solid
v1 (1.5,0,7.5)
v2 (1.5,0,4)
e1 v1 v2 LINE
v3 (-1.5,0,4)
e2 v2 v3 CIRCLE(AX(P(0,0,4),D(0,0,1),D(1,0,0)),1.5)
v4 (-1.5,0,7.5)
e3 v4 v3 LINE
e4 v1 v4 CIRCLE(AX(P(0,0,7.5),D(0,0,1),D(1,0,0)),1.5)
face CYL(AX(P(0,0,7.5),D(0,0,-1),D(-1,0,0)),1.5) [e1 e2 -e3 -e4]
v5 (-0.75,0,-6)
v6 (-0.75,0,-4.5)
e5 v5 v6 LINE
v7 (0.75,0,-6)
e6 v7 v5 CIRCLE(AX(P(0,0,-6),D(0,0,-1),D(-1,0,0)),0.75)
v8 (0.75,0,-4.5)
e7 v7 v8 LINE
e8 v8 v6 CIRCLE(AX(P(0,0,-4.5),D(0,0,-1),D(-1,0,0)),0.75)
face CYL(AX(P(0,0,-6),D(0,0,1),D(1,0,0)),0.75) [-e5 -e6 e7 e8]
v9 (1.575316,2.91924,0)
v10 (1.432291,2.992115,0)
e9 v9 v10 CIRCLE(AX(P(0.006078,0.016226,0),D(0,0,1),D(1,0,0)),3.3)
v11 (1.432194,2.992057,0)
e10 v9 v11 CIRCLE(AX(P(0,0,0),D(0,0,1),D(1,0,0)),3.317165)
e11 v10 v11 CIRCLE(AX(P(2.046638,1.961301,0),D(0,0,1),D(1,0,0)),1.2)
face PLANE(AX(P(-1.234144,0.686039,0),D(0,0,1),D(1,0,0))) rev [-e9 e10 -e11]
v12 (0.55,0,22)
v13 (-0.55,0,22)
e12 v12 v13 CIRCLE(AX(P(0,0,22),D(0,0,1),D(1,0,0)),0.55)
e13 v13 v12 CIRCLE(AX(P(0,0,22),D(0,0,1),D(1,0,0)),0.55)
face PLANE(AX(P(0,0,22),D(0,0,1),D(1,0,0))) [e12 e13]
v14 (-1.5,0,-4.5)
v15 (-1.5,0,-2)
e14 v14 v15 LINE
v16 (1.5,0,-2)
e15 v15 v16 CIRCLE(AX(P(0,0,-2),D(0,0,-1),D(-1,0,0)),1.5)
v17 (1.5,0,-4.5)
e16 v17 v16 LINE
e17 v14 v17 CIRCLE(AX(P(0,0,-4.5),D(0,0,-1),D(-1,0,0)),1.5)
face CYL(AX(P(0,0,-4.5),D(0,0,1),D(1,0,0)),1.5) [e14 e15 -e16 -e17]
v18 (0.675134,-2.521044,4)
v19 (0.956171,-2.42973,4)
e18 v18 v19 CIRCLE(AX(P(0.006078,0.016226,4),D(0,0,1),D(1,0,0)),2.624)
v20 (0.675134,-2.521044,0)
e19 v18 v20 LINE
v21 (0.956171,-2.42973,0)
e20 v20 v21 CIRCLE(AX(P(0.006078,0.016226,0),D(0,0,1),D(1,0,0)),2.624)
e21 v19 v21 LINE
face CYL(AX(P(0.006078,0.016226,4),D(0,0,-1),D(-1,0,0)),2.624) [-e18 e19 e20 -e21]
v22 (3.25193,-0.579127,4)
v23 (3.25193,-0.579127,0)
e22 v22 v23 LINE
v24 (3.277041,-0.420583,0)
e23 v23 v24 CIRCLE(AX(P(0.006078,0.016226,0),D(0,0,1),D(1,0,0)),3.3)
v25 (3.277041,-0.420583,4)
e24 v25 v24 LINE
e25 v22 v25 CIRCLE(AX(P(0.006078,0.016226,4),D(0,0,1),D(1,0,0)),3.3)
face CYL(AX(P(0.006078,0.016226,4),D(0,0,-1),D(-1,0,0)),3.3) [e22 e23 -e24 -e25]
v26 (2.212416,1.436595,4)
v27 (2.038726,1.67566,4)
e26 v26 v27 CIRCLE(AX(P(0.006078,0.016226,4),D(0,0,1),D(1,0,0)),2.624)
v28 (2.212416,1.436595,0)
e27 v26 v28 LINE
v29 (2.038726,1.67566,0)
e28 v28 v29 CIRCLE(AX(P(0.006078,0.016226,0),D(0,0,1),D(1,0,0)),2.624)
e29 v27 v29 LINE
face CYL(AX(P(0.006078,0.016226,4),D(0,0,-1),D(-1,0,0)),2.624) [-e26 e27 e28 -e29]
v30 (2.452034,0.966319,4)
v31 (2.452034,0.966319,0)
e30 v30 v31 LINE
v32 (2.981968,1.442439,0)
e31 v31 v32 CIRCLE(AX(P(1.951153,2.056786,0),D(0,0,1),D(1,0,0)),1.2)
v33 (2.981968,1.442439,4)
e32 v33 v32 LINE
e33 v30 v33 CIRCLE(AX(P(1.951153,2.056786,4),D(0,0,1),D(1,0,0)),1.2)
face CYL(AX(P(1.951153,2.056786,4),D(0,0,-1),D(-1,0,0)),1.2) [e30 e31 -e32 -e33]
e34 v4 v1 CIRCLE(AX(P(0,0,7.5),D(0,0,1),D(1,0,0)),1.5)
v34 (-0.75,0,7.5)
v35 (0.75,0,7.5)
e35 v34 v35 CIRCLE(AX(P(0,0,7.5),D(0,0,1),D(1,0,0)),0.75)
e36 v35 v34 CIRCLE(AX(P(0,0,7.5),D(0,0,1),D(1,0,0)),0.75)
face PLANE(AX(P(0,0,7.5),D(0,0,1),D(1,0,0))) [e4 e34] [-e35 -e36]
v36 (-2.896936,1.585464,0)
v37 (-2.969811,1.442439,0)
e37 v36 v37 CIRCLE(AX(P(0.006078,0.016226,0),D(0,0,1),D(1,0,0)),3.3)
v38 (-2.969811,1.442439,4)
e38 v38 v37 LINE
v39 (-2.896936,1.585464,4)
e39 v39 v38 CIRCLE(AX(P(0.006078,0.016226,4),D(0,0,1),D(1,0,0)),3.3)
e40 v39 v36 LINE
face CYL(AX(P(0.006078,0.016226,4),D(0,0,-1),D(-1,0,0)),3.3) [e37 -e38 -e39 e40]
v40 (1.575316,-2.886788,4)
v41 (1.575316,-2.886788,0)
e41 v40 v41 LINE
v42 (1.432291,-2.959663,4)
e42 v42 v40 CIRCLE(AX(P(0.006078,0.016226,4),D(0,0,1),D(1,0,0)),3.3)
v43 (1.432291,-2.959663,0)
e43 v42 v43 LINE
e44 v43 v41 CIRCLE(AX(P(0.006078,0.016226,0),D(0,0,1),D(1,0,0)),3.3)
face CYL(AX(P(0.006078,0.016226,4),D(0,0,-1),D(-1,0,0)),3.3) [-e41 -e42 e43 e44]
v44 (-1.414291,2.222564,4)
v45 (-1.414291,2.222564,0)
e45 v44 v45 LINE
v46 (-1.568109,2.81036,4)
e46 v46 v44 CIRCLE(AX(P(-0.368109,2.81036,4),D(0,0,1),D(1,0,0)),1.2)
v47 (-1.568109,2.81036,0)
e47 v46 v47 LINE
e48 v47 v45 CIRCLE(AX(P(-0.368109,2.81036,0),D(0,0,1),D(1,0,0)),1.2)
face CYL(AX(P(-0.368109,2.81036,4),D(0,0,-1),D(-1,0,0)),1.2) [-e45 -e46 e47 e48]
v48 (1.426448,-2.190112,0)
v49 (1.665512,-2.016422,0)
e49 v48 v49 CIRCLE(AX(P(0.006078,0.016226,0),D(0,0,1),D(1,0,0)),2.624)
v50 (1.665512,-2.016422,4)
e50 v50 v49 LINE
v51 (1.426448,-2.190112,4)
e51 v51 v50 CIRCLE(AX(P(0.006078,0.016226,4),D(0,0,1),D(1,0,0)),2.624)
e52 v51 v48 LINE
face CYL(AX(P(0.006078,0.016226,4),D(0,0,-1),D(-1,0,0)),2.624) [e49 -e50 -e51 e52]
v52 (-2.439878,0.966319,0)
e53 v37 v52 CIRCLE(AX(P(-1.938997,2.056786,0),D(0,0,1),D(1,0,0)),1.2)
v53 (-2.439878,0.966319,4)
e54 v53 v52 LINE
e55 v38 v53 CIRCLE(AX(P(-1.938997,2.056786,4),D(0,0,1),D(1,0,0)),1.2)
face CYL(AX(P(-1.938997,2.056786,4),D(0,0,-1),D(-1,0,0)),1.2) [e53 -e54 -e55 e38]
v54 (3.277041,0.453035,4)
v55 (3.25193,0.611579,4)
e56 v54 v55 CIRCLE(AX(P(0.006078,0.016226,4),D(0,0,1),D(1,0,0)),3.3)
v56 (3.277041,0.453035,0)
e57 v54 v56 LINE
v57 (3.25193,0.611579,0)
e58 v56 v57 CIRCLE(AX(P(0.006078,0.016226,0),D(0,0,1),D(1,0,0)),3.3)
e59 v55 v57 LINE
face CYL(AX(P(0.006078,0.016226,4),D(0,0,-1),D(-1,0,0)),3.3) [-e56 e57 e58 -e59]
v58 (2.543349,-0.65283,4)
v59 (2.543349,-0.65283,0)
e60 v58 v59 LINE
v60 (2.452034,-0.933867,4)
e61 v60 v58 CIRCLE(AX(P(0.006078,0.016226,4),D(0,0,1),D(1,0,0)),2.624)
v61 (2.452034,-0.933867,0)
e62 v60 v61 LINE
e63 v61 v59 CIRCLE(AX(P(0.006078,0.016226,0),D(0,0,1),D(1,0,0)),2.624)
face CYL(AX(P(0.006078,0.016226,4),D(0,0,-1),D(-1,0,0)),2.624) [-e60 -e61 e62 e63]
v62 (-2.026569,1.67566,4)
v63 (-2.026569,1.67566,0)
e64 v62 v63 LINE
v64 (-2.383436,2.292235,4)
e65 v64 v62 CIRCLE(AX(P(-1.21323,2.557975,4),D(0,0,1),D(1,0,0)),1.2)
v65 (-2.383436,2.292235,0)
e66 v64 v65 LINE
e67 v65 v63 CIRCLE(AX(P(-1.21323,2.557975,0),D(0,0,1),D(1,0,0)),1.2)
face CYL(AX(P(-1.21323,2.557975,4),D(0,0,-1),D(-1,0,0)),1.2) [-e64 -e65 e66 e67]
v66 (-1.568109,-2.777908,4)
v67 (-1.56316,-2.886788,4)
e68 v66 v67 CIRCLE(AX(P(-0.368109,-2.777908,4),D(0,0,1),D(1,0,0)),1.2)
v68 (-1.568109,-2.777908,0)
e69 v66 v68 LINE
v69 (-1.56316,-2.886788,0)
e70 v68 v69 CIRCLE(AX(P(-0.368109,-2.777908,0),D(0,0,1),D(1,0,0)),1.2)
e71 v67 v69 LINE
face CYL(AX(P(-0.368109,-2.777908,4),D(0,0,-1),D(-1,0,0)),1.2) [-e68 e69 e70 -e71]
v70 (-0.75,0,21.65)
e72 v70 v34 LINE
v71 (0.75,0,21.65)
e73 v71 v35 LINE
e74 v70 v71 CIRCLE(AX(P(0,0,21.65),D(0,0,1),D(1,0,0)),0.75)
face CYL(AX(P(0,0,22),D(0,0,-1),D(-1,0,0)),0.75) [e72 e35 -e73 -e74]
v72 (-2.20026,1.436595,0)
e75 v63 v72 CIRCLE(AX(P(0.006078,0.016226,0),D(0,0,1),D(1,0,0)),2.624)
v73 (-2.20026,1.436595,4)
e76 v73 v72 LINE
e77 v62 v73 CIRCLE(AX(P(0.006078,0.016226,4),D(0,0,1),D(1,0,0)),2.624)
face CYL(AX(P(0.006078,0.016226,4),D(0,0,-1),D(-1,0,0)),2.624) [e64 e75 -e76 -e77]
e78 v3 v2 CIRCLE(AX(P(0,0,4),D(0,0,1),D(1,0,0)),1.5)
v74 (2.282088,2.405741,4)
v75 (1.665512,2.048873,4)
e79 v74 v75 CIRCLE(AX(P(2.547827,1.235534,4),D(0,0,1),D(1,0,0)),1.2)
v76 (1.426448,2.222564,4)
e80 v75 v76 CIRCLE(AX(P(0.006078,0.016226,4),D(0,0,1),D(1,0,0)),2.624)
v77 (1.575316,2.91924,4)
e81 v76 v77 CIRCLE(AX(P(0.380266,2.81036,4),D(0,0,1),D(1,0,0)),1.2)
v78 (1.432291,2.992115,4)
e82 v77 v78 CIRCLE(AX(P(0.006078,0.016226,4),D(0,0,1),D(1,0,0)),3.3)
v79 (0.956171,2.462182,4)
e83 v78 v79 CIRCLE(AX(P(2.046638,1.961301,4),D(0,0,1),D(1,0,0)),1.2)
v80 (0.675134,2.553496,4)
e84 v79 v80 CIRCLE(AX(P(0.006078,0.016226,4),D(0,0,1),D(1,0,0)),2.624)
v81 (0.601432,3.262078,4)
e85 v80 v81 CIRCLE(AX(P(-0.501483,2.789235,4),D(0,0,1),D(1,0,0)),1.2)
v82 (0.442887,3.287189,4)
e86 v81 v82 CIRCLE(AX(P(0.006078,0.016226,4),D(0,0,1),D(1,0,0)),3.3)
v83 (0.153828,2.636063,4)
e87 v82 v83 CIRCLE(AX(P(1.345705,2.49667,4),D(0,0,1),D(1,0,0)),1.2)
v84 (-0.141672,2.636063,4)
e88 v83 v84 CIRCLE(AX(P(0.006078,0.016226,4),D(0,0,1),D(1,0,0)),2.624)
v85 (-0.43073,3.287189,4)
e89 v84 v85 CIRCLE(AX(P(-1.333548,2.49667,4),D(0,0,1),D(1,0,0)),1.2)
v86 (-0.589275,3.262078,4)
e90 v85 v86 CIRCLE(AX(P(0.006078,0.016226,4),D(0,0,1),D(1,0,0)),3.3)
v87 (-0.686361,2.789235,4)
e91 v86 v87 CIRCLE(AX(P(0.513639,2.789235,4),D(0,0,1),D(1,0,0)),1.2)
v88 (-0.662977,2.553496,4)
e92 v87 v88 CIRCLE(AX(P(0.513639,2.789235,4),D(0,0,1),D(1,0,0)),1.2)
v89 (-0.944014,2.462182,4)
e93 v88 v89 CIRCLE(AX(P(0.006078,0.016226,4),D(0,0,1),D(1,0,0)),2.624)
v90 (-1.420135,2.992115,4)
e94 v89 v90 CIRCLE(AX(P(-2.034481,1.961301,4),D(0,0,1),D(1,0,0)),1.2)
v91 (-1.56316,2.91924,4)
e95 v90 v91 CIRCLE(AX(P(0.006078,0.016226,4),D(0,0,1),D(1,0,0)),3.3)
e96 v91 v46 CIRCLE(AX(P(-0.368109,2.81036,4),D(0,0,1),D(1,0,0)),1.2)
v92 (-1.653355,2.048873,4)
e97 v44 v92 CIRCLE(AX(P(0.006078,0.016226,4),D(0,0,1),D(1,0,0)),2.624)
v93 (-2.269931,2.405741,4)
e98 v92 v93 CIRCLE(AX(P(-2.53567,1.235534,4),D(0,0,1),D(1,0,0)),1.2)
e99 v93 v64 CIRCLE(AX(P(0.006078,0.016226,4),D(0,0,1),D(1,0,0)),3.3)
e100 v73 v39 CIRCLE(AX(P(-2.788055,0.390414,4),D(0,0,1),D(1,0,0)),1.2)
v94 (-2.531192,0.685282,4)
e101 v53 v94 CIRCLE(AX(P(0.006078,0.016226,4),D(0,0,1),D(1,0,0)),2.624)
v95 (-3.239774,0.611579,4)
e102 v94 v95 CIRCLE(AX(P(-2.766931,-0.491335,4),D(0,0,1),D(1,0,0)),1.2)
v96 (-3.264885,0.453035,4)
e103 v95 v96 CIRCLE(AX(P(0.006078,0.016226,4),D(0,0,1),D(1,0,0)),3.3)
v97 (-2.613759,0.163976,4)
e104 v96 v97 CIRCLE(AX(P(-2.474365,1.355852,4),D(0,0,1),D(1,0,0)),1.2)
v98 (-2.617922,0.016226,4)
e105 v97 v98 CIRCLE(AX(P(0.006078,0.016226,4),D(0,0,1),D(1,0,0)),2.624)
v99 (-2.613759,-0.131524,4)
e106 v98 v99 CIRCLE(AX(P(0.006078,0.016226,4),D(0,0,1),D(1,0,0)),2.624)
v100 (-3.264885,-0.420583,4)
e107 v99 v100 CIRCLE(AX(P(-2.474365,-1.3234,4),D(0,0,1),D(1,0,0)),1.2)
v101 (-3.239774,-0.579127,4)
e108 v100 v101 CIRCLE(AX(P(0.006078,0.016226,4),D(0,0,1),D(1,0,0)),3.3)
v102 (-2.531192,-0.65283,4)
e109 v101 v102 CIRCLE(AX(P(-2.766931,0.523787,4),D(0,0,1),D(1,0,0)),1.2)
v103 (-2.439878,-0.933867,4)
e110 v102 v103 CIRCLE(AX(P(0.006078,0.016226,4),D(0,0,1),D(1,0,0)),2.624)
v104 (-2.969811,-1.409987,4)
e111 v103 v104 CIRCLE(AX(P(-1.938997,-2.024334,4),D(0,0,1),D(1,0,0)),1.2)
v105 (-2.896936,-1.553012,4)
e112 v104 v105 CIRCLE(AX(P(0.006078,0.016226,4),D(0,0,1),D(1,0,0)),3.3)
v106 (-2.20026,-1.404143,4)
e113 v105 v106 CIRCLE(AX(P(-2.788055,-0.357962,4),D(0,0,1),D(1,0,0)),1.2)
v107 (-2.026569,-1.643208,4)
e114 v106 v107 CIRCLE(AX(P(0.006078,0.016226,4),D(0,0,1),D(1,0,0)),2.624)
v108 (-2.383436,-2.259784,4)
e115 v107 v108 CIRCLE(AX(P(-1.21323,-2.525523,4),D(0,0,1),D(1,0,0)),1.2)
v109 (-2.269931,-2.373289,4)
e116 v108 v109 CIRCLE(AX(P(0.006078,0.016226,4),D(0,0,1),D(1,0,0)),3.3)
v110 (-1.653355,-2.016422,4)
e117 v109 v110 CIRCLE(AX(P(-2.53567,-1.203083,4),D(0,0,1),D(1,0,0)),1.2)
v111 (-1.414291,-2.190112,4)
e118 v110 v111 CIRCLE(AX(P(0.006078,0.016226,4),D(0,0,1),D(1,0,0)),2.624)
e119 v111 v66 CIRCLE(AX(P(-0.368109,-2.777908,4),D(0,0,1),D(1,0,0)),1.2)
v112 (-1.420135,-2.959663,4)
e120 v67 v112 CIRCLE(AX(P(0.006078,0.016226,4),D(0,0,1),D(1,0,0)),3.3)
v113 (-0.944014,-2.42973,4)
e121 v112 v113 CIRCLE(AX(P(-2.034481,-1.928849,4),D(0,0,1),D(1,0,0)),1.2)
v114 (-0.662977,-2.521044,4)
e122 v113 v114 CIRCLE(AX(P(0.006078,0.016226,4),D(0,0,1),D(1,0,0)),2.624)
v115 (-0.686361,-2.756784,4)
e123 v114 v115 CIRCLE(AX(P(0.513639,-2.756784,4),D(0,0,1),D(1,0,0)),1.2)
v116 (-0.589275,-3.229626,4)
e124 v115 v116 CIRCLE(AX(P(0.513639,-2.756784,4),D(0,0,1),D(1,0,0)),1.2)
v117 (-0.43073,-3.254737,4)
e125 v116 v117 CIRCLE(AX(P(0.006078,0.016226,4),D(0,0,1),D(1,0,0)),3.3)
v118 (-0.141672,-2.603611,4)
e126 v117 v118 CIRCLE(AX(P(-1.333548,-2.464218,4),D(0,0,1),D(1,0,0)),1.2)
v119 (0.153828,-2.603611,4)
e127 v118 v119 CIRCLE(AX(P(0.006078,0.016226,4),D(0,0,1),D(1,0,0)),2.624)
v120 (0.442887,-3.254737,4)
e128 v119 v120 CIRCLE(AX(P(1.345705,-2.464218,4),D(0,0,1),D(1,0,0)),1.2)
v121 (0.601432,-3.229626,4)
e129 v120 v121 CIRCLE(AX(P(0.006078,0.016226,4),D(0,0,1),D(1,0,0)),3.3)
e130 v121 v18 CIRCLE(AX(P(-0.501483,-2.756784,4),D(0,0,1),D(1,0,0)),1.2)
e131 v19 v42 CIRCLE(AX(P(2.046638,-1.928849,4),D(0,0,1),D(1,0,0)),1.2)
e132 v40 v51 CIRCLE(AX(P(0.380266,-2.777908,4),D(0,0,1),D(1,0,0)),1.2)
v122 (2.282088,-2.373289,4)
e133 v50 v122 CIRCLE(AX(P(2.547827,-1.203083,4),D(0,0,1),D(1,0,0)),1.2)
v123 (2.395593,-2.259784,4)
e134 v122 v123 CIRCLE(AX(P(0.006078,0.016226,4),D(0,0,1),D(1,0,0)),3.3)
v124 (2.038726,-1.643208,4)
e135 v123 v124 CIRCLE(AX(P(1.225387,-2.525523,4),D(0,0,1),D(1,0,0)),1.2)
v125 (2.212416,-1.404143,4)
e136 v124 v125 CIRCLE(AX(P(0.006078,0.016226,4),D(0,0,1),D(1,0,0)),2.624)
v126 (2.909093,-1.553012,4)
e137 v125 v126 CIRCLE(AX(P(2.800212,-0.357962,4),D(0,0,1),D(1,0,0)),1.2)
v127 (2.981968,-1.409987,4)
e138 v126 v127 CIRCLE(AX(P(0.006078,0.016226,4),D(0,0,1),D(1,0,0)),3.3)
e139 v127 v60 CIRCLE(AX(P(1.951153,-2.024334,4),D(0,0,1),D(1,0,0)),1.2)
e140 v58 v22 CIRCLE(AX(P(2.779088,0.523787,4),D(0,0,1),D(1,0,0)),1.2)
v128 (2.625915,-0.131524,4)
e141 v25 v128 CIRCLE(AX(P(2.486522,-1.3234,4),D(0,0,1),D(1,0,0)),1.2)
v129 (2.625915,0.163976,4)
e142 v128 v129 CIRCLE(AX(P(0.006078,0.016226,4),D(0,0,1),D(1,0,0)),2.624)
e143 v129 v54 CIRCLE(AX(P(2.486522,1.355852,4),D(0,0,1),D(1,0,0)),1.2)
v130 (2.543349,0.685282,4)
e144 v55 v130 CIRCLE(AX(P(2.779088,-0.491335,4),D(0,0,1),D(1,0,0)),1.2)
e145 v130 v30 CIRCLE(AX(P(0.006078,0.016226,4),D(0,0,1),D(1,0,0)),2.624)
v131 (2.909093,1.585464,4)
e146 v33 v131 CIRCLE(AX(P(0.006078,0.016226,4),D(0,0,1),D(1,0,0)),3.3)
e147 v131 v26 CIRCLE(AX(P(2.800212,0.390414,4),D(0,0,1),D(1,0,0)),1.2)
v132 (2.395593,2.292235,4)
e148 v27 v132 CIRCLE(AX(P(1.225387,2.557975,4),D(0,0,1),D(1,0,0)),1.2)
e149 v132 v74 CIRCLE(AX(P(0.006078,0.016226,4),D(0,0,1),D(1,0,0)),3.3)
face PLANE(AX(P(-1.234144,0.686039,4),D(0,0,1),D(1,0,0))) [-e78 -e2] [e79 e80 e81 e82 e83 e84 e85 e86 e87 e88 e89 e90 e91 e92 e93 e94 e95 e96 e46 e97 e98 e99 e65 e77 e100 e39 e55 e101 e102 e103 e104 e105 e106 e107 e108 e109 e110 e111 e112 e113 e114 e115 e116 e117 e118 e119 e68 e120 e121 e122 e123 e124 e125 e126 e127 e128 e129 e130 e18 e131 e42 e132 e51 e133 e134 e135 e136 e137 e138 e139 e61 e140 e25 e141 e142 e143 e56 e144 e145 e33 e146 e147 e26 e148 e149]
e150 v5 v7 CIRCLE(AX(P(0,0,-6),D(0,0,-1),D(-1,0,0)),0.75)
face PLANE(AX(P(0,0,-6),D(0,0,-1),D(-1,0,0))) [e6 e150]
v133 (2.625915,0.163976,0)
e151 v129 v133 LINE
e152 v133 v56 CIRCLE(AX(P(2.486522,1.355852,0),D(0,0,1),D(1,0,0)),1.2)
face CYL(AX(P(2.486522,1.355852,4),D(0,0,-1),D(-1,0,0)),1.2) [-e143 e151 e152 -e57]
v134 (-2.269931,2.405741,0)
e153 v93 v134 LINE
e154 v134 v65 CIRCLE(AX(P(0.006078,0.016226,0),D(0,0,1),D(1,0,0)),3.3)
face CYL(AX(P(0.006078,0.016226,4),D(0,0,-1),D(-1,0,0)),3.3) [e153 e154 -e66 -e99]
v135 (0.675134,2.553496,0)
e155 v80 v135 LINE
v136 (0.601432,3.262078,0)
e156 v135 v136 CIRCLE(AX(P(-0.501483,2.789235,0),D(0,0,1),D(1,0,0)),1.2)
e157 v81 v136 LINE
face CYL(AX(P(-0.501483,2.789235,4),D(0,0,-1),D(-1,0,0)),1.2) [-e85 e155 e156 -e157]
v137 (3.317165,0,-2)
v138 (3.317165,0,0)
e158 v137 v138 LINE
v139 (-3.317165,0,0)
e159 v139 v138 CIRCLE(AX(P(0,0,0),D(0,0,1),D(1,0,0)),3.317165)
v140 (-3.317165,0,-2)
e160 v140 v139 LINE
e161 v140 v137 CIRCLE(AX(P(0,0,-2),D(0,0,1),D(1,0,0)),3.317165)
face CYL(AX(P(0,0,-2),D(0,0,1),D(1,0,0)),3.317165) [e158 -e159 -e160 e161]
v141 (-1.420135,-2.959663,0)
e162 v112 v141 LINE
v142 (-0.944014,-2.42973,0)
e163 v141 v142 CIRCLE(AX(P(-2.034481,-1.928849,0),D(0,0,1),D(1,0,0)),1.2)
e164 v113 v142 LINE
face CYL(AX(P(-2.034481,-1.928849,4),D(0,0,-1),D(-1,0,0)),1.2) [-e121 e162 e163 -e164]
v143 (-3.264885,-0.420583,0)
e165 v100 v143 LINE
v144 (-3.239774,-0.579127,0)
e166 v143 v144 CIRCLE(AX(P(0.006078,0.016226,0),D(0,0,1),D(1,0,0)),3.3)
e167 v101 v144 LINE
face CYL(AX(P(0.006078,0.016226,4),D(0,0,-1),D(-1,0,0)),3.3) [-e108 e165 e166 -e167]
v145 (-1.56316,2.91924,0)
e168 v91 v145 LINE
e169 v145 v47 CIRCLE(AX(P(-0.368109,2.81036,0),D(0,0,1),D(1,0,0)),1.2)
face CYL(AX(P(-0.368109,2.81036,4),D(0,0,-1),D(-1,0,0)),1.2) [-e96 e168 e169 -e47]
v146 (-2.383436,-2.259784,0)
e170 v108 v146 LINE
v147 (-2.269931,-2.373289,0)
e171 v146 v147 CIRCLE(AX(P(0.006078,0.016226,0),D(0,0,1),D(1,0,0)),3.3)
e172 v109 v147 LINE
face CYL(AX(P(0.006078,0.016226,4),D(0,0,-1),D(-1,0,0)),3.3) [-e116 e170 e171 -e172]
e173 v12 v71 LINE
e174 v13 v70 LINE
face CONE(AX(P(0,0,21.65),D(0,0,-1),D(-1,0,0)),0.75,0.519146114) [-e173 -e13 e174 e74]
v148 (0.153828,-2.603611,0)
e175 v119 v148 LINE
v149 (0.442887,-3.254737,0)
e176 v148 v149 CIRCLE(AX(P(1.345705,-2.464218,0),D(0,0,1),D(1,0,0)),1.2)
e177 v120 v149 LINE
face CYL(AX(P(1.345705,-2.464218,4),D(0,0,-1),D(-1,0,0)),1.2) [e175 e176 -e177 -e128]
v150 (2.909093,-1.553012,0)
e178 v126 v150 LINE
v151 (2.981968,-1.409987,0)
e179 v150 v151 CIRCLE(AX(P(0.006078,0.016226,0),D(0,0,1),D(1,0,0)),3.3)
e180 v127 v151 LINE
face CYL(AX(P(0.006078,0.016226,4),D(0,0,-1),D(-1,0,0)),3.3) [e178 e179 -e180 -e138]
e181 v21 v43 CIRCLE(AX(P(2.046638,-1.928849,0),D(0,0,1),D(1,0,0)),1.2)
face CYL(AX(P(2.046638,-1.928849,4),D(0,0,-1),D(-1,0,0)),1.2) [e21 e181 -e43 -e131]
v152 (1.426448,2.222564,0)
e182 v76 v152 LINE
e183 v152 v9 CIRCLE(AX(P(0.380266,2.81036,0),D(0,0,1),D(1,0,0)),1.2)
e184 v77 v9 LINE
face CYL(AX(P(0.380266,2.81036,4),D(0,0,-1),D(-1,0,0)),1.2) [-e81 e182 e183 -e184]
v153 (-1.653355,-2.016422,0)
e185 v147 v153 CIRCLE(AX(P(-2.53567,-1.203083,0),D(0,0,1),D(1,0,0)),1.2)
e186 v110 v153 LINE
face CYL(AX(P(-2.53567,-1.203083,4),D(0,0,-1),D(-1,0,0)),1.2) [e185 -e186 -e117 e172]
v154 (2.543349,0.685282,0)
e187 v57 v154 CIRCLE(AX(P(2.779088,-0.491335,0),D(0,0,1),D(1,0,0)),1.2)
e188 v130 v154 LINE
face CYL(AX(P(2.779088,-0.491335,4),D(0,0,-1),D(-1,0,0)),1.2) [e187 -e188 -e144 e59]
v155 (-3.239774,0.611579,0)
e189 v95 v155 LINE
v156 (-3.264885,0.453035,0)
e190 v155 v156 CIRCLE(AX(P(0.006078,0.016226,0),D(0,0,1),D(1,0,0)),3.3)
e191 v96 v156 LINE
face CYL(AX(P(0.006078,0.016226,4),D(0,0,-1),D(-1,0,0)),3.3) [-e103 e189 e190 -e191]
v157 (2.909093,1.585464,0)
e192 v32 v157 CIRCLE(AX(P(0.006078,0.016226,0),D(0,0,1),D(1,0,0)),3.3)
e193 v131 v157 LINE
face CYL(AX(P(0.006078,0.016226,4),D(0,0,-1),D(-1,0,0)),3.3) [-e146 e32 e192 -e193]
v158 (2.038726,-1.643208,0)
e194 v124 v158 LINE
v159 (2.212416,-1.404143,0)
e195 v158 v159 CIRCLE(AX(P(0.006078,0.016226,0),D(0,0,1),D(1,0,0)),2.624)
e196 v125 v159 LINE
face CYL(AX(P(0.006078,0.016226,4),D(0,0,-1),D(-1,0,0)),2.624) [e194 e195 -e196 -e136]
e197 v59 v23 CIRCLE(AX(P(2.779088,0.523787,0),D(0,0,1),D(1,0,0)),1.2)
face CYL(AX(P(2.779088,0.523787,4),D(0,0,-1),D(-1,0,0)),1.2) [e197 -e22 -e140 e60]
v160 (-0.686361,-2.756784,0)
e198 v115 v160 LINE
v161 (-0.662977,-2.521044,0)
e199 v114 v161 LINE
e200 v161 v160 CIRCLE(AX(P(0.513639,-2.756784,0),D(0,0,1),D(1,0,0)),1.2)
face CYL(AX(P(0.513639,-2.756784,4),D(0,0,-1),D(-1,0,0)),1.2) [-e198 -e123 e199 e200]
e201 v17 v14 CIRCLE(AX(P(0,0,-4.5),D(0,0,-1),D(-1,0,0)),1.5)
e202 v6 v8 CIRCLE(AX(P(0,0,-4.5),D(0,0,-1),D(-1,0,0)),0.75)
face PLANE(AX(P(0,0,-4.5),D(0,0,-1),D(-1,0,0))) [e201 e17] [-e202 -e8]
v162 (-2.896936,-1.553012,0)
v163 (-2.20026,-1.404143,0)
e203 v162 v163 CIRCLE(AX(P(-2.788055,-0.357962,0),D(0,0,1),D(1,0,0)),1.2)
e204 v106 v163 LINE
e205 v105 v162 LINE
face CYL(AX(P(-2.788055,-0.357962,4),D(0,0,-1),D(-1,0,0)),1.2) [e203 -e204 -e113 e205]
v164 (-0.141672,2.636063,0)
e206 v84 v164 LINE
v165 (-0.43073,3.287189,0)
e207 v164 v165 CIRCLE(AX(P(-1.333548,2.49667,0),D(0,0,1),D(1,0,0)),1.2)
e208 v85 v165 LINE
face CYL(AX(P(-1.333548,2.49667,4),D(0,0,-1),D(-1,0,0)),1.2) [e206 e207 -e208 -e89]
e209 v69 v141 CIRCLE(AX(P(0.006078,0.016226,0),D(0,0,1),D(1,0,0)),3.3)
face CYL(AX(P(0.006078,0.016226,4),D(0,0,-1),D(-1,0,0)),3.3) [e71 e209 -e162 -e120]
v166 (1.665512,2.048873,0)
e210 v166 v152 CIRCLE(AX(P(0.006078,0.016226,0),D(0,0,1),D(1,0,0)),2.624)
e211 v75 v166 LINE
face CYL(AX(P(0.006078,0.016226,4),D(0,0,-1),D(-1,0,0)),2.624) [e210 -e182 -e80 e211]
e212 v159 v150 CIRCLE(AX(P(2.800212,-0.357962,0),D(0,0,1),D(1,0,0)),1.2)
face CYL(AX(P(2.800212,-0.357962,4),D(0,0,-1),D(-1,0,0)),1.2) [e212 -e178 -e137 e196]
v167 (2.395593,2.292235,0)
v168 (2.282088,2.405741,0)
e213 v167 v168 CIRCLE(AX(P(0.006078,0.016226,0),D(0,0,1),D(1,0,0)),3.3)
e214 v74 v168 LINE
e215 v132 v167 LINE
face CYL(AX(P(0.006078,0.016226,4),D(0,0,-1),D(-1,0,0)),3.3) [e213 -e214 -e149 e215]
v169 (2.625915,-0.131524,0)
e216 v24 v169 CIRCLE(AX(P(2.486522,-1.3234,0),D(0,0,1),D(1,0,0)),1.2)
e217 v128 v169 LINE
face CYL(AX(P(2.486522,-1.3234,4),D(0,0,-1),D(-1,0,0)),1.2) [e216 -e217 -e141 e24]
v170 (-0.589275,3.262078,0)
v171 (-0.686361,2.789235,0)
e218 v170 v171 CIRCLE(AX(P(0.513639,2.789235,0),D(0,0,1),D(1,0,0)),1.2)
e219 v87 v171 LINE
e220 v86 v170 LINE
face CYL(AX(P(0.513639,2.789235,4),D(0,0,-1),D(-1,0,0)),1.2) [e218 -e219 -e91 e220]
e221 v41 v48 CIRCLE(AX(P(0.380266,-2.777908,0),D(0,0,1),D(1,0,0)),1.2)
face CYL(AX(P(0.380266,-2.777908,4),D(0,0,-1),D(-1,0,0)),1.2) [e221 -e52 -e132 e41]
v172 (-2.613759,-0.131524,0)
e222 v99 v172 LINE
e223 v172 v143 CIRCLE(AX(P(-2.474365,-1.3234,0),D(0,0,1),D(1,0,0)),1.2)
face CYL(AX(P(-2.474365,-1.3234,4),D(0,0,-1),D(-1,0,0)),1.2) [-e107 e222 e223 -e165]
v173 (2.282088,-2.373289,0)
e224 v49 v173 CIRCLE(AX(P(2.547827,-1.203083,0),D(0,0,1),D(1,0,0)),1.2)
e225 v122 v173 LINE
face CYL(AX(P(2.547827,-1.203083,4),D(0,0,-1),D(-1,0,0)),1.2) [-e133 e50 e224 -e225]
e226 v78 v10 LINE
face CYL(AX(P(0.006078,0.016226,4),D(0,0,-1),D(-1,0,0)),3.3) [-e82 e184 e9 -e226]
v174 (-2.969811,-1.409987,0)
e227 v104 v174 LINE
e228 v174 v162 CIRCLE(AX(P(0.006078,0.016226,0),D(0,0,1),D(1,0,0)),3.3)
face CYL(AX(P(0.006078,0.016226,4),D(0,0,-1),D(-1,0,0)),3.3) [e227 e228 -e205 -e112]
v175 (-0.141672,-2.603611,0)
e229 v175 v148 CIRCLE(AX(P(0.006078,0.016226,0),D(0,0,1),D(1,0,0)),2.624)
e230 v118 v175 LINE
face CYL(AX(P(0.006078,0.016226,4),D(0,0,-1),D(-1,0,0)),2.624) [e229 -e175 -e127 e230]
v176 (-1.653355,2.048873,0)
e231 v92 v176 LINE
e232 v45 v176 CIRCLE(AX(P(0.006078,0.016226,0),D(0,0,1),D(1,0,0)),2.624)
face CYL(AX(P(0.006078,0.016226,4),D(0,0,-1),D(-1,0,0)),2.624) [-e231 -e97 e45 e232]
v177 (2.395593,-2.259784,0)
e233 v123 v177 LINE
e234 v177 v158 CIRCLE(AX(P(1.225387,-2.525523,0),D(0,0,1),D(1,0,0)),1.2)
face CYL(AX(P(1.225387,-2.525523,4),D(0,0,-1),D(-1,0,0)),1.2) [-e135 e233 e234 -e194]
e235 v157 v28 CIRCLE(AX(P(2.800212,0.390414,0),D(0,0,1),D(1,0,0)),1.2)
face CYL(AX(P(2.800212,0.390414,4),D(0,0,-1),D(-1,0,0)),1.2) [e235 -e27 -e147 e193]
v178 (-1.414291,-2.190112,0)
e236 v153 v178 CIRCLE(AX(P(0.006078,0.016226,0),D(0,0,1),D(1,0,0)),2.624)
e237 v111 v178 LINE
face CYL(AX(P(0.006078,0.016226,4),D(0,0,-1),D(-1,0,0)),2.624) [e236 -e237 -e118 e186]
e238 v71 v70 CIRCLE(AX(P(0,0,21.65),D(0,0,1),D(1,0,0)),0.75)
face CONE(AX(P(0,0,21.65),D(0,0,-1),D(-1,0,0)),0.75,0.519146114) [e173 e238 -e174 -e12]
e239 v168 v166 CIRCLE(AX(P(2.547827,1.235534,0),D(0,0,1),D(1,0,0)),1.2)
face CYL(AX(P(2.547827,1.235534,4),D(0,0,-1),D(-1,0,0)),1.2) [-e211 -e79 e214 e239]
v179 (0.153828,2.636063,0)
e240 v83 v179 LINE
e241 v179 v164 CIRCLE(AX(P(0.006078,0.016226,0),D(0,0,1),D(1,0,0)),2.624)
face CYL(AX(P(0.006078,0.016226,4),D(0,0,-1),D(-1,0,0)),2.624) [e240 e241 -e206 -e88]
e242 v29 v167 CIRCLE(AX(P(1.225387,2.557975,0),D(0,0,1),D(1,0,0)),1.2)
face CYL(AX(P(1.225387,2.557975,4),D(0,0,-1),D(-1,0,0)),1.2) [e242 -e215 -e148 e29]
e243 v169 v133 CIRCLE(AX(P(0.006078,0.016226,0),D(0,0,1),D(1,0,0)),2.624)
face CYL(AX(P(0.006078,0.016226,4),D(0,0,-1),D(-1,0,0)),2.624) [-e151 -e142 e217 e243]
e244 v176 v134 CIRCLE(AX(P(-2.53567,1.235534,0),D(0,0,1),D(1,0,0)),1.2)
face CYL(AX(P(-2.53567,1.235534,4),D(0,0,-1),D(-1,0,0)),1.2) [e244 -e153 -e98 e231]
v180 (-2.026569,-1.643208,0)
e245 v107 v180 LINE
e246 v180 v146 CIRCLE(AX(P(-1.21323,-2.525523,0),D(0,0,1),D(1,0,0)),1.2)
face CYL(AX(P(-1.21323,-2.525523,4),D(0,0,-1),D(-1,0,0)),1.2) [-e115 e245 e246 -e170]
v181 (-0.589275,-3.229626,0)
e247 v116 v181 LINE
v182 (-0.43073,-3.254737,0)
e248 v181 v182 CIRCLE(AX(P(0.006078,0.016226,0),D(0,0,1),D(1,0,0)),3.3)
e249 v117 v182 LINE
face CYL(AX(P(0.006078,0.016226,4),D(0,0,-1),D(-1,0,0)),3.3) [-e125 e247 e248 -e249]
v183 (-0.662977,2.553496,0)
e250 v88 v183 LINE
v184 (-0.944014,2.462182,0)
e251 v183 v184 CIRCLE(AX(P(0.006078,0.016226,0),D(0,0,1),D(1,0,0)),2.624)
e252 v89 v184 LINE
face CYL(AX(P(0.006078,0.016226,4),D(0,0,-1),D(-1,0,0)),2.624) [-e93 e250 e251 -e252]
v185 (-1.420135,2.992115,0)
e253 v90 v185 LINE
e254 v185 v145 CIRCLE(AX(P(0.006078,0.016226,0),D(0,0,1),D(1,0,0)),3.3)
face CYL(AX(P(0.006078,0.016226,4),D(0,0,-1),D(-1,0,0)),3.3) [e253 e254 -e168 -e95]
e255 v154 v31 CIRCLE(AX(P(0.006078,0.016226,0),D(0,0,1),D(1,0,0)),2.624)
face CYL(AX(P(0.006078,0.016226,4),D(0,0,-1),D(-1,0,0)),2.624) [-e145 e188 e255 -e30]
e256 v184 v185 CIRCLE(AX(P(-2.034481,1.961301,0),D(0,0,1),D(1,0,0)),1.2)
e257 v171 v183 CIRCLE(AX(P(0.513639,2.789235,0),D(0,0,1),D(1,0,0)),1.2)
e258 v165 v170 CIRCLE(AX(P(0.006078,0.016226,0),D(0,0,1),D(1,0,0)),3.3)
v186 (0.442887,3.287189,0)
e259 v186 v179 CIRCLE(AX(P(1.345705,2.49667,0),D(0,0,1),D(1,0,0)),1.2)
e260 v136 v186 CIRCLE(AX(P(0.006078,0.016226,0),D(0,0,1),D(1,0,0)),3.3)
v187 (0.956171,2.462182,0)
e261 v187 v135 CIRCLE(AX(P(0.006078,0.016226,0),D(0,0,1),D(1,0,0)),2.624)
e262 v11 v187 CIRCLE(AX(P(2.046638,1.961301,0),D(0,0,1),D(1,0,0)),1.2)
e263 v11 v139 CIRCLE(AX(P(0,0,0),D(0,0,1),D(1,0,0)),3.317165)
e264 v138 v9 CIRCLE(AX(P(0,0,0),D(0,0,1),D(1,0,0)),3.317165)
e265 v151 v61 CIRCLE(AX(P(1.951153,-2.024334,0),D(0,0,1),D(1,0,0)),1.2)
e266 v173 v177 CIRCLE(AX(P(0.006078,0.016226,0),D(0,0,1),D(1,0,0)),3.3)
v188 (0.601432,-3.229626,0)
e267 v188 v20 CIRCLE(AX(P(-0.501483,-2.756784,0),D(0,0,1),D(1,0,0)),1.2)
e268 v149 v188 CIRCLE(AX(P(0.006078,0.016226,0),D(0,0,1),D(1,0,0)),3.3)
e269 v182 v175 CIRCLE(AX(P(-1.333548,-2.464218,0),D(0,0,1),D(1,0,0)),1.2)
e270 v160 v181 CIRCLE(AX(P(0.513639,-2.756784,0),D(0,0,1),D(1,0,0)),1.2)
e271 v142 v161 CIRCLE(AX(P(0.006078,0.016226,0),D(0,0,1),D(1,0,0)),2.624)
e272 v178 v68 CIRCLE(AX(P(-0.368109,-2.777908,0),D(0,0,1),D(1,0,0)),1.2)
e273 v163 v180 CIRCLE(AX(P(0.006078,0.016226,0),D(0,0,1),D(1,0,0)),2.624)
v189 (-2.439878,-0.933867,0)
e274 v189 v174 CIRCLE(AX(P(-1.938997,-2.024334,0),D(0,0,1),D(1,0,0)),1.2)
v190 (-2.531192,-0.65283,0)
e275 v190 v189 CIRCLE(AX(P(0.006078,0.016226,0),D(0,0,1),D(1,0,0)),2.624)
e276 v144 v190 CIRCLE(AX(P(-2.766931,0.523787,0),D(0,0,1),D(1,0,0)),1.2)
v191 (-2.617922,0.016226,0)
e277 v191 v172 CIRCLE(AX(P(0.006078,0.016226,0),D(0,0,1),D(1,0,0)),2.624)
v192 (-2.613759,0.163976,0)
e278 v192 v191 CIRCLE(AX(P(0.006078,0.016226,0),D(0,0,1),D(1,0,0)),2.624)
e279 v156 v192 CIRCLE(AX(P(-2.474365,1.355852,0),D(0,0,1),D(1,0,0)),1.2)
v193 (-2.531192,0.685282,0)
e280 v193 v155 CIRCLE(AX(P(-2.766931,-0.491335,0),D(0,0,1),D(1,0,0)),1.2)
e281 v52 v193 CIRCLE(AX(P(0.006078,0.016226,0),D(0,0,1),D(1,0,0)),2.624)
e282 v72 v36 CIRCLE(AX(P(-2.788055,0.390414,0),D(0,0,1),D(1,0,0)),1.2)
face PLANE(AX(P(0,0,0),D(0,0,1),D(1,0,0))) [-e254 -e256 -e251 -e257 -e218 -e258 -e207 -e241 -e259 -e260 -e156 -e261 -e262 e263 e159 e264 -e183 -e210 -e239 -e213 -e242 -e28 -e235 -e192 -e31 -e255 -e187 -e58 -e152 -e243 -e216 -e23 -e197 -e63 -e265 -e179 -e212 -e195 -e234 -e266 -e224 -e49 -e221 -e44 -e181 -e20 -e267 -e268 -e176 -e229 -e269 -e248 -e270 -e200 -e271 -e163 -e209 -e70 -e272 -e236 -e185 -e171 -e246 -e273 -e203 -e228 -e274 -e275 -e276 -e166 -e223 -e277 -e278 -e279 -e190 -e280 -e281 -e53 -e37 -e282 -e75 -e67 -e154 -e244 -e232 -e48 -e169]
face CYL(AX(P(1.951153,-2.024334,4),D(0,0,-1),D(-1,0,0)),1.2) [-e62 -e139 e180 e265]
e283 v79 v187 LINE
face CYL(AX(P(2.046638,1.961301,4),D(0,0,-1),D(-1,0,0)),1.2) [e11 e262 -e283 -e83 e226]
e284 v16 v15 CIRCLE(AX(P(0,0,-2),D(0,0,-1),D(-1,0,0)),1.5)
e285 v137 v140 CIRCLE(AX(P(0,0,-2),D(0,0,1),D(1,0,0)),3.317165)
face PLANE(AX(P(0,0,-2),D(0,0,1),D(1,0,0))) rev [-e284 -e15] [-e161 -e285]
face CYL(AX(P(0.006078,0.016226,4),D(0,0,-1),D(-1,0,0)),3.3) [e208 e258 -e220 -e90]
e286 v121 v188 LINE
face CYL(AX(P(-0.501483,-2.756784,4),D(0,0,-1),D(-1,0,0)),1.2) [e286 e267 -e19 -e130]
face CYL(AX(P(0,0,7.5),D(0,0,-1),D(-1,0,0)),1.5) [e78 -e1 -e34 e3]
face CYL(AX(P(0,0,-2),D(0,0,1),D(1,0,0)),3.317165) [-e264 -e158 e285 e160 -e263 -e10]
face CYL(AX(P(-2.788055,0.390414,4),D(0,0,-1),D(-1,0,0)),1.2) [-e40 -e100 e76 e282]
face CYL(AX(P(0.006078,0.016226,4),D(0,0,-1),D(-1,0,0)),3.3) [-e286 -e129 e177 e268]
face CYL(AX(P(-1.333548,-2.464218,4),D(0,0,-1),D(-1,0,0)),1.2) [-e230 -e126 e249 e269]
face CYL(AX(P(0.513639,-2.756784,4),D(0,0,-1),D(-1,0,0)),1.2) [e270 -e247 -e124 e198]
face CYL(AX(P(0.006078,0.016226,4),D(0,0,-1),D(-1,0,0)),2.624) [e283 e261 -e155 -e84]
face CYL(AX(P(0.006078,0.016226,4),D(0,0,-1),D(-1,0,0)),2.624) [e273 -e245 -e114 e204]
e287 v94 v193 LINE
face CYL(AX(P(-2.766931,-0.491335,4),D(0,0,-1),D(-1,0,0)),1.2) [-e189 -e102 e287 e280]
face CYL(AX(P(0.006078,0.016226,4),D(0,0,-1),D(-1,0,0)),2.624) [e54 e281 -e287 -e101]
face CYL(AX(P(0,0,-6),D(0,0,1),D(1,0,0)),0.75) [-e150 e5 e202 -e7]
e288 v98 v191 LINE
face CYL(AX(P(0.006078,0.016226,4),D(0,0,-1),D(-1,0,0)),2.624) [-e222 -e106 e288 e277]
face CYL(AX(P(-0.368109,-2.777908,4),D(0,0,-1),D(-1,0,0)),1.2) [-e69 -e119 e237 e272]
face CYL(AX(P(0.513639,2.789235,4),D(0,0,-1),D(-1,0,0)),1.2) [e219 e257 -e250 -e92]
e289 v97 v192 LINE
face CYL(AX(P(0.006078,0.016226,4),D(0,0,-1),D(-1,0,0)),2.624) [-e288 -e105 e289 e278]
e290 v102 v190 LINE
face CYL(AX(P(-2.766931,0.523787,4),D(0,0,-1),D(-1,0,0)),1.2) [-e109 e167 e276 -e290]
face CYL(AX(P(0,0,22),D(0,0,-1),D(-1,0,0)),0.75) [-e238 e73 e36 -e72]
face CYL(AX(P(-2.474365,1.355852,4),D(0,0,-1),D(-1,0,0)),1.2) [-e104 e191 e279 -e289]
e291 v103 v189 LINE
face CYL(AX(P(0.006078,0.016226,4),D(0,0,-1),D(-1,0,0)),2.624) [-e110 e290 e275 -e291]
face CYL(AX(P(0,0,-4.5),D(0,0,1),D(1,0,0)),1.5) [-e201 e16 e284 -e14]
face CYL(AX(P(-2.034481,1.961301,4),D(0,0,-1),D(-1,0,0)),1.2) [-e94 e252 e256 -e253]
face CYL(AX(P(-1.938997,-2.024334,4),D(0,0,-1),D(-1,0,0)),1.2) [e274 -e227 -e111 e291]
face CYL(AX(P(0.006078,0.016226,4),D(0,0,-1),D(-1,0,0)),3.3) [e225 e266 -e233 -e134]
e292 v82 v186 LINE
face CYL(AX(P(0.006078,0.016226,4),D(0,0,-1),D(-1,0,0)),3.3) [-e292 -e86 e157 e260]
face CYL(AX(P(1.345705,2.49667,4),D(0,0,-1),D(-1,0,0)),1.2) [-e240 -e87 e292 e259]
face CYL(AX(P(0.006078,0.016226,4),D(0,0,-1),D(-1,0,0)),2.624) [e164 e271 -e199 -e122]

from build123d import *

# Parameters (mm, degrees)
BOSS_EXTRUDE_1_DEPTH = 4
SKETCH_3_R           = 3.317165214
BOSS_EXTRUDE_2_DEPTH = 2
SKETCH_4_R           = 1.5
BOSS_EXTRUDE_3_DEPTH = 2.5
BOSS_EXTRUDE_START   = 3.5
SKETCH_5_R           = 1.5
BOSS_EXTRUDE_4_DEPTH = 3.5
SKETCH_6_R           = 0.75
BOSS_EXTRUDE_5_DEPTH = 1.5
BOSS_EXTRUDE_START_2 = 14.5
SKETCH_7_R           = 0.75
BOSS_EXTRUDE_6_DEPTH = 14.5


with BuildPart() as part:
    # Sketch 1 → Boss-Extrude 1 (new body)
    with BuildSketch(Plane.XY):
        with BuildLine():
            ThreePointArc((-3.264884569, 0.453034732), (-2.961266903, 0.259072006), (-2.613758715, 0.163975816))
            ThreePointArc((-2.613758715, 0.163975816), (-2.617921702, 0.016225934), (-2.613758715, -0.131523948))
            ThreePointArc((-2.613758715, -0.131523948), (-2.961266903, -0.226620138), (-3.264884569, -0.420582864))
            ThreePointArc((-3.264884569, -0.420582864), (-3.253293226, -0.500007801), (-3.239773593, -0.579127326))
            ThreePointArc((-3.239773593, -0.579127326), (-2.891078254, -0.669773822), (-2.531191989, -0.652829737))
            ThreePointArc((-2.531191989, -0.652829737), (-2.489494001, -0.794634659), (-2.43987754, -0.933866714))
            ThreePointArc((-2.43987754, -0.933866714), (-2.740991128, -1.1316945), (-2.969810909, -1.409987033))
            ThreePointArc((-2.969810909, -1.409987033), (-2.934243232, -1.481942715), (-2.896936018, -1.553012059))
            ThreePointArc((-2.896936018, -1.553012059), (-2.537295737, -1.531469214), (-2.200259569, -1.40414346))
            ThreePointArc((-2.200259569, -1.40414346), (-2.116782295, -1.526122568), (-2.026569166, -1.643207791))
            ThreePointArc((-2.026569166, -1.643207791), (-2.251813058, -1.924402412), (-2.38343648, -2.25978354))
            ThreePointArc((-2.38343648, -2.25978354), (-2.32737408, -2.317226444), (-2.269931176, -2.373288844))
            ThreePointArc((-2.269931176, -2.373288844), (-1.934550048, -2.241665422), (-1.653355427, -2.01642153))
            ThreePointArc((-1.653355427, -2.01642153), (-1.536270204, -2.106634659), (-1.414291096, -2.190111933))
            ThreePointArc((-1.414291096, -2.190111933), (-1.54161685, -2.527148101), (-1.563159695, -2.886788382))
            ThreePointArc((-1.563159695, -2.886788382), (-1.492090351, -2.924095596), (-1.420134669, -2.959663273))
            ThreePointArc((-1.420134669, -2.959663273), (-1.141842136, -2.730843492), (-0.94401435, -2.429729904))
            ThreePointArc((-0.94401435, -2.429729904), (-0.804782295, -2.479346365), (-0.662977373, -2.521044353))
            ThreePointArc((-0.662977373, -2.521044353), (-0.679921458, -2.880930618), (-0.589274962, -3.229625956))
            ThreePointArc((-0.589274962, -3.229625956), (-0.510155437, -3.24314559), (-0.4307305, -3.254736932))
            ThreePointArc((-0.4307305, -3.254736932), (-0.236767774, -2.951119267), (-0.141671584, -2.603611078))
            ThreePointArc((-0.141671584, -2.603611078), (0.006078298, -2.607774066), (0.15382818, -2.603611078))
            ThreePointArc((0.15382818, -2.603611078), (0.24892437, -2.951119267), (0.442887096, -3.254736932))
            ThreePointArc((0.442887096, -3.254736932), (0.522312033, -3.24314559), (0.601431558, -3.229625956))
            ThreePointArc((0.601431558, -3.229625956), (0.692078054, -2.880930618), (0.675133969, -2.521044353))
            ThreePointArc((0.675133969, -2.521044353), (0.816938891, -2.479346365), (0.956170946, -2.429729904))
            ThreePointArc((0.956170946, -2.429729904), (1.153998732, -2.730843492), (1.432291265, -2.959663273))
            ThreePointArc((1.432291265, -2.959663273), (1.504246947, -2.924095596), (1.575316291, -2.886788382))
            ThreePointArc((1.575316291, -2.886788382), (1.553773446, -2.527148101), (1.426447692, -2.190111933))
            ThreePointArc((1.426447692, -2.190111933), (1.5484268, -2.106634659), (1.665512023, -2.01642153))
            ThreePointArc((1.665512023, -2.01642153), (1.946706645, -2.241665422), (2.282087772, -2.373288844))
            ThreePointArc((2.282087772, -2.373288844), (2.339530676, -2.317226444), (2.395593076, -2.25978354))
            ThreePointArc((2.395593076, -2.25978354), (2.263969654, -1.924402412), (2.038725762, -1.643207791))
            ThreePointArc((2.038725762, -1.643207791), (2.128938891, -1.526122568), (2.212416166, -1.40414346))
            ThreePointArc((2.212416166, -1.40414346), (2.549452333, -1.531469214), (2.909092614, -1.553012059))
            ThreePointArc((2.909092614, -1.553012059), (2.946399828, -1.481942715), (2.981967505, -1.409987033))
            ThreePointArc((2.981967505, -1.409987033), (2.753147724, -1.1316945), (2.452034136, -0.933866714))
            ThreePointArc((2.452034136, -0.933866714), (2.501650597, -0.794634659), (2.543348585, -0.652829737))
            ThreePointArc((2.543348585, -0.652829737), (2.90323485, -0.669773822), (3.251930189, -0.579127326))
            ThreePointArc((3.251930189, -0.579127326), (3.265449822, -0.500007801), (3.277041165, -0.420582864))
            ThreePointArc((3.277041165, -0.420582864), (2.973423499, -0.226620138), (2.625915311, -0.131523948))
            ThreePointArc((2.625915311, -0.131523948), (2.630078298, 0.016225934), (2.625915311, 0.163975816))
            ThreePointArc((2.625915311, 0.163975816), (2.973423499, 0.259072006), (3.277041165, 0.453034732))
            ThreePointArc((3.277041165, 0.453034732), (3.265449822, 0.532459669), (3.251930189, 0.611579194))
            ThreePointArc((3.251930189, 0.611579194), (2.90323485, 0.70222569), (2.543348585, 0.685281605))
            ThreePointArc((2.543348585, 0.685281605), (2.501650597, 0.827086527), (2.452034136, 0.966318582))
            ThreePointArc((2.452034136, 0.966318582), (2.753147724, 1.164146368), (2.981967505, 1.442438901))
            ThreePointArc((2.981967505, 1.442438901), (2.946399828, 1.514394583), (2.909092614, 1.585463927))
            ThreePointArc((2.909092614, 1.585463927), (2.549452333, 1.563921082), (2.212416166, 1.436595328))
            ThreePointArc((2.212416166, 1.436595328), (2.128938891, 1.558574436), (2.038725762, 1.675659659))
            ThreePointArc((2.038725762, 1.675659659), (2.263969654, 1.956854281), (2.395593076, 2.292235408))
            ThreePointArc((2.395593076, 2.292235408), (2.339530676, 2.349678312), (2.282087772, 2.405740712))
            ThreePointArc((2.282087772, 2.405740712), (1.946706645, 2.27411729), (1.665512023, 2.048873398))
            ThreePointArc((1.665512023, 2.048873398), (1.5484268, 2.139086527), (1.426447692, 2.222563802))
            ThreePointArc((1.426447692, 2.222563802), (1.553773446, 2.559599969), (1.575316291, 2.91924025))
            ThreePointArc((1.575316291, 2.91924025), (1.504246947, 2.956547464), (1.432291265, 2.992115141))
            ThreePointArc((1.432291265, 2.992115141), (1.153998732, 2.76329536), (0.956170946, 2.462181772))
            ThreePointArc((0.956170946, 2.462181772), (0.816938891, 2.511798233), (0.675133969, 2.553496221))
            ThreePointArc((0.675133969, 2.553496221), (0.692078054, 2.913382486), (0.601431558, 3.262077825))
            ThreePointArc((0.601431558, 3.262077825), (0.522312033, 3.275597458), (0.442887096, 3.287188801))
            ThreePointArc((0.442887096, 3.287188801), (0.24892437, 2.983571135), (0.15382818, 2.636062947))
            ThreePointArc((0.15382818, 2.636062947), (0.006078298, 2.640225934), (-0.141671584, 2.636062947))
            ThreePointArc((-0.141671584, 2.636062947), (-0.236767774, 2.983571135), (-0.4307305, 3.287188801))
            ThreePointArc((-0.4307305, 3.287188801), (-0.510155437, 3.275597458), (-0.589274962, 3.262077825))
            ThreePointArc((-0.589274962, 3.262077825), (-0.679921458, 2.913382486), (-0.662977373, 2.553496221))
            ThreePointArc((-0.662977373, 2.553496221), (-0.804782295, 2.511798233), (-0.94401435, 2.462181772))
            ThreePointArc((-0.94401435, 2.462181772), (-1.141842136, 2.76329536), (-1.420134669, 2.992115141))
            ThreePointArc((-1.420134669, 2.992115141), (-1.492090351, 2.956547464), (-1.563159695, 2.91924025))
            ThreePointArc((-1.563159695, 2.91924025), (-1.54161685, 2.559599969), (-1.414291096, 2.222563802))
            ThreePointArc((-1.414291096, 2.222563802), (-1.536270204, 2.139086527), (-1.653355427, 2.048873398))
            ThreePointArc((-1.653355427, 2.048873398), (-1.934550048, 2.27411729), (-2.269931176, 2.405740712))
            ThreePointArc((-2.269931176, 2.405740712), (-2.32737408, 2.349678312), (-2.38343648, 2.292235408))
            ThreePointArc((-2.38343648, 2.292235408), (-2.251813058, 1.956854281), (-2.026569166, 1.675659659))
            ThreePointArc((-2.026569166, 1.675659659), (-2.116782295, 1.558574436), (-2.200259569, 1.436595328))
            ThreePointArc((-2.200259569, 1.436595328), (-2.537295737, 1.563921082), (-2.896936018, 1.585463927))
            ThreePointArc((-2.896936018, 1.585463927), (-2.934243232, 1.514394583), (-2.969810909, 1.442438901))
            ThreePointArc((-2.969810909, 1.442438901), (-2.740991128, 1.164146368), (-2.43987754, 0.966318582))
            ThreePointArc((-2.43987754, 0.966318582), (-2.489494001, 0.827086527), (-2.531191989, 0.685281605))
            ThreePointArc((-2.531191989, 0.685281605), (-2.891078254, 0.70222569), (-3.239773593, 0.611579194))
            ThreePointArc((-3.239773593, 0.611579194), (-3.253293226, 0.532459669), (-3.264884569, 0.453034732))
        make_face()
    extrude(amount=BOSS_EXTRUDE_1_DEPTH)

    # Sketch 3 → Boss-Extrude 2 (add)
    with BuildSketch(Plane.XY):
        Circle(SKETCH_3_R)
    extrude(amount=-BOSS_EXTRUDE_2_DEPTH)

    # Sketch 4 → Boss-Extrude 3 (add)
    with BuildSketch(Plane(origin=(0, 0, -2), x_dir=(-1, 0, 0), z_dir=(0, 0, -1))):
        Circle(SKETCH_4_R)
    extrude(amount=BOSS_EXTRUDE_3_DEPTH)

    # Sketch 5 → Boss-Extrude 4 (add)
    with BuildSketch(Plane.XY.offset(4).offset(BOSS_EXTRUDE_START)):
        with Locations(Location((0, 0, 0), (0, 0, 180))):
            Circle(SKETCH_5_R)
    extrude(amount=-BOSS_EXTRUDE_4_DEPTH)

    # Sketch 6 → Boss-Extrude 5 (add)
    with BuildSketch(Plane(origin=(0, 0, -4.5), x_dir=(-1, 0, 0), z_dir=(0, 0, -1))):
        Circle(SKETCH_6_R)
    extrude(amount=BOSS_EXTRUDE_5_DEPTH)

    # Sketch 7 → Boss-Extrude 6 (add)
    with BuildSketch(Plane.XY.offset(7.5).offset(BOSS_EXTRUDE_START_2)):
        with Locations(Location((0, 0, 0), (0, 0, 180))):
            Circle(SKETCH_7_R)
    extrude(amount=-BOSS_EXTRUDE_6_DEPTH)

    # Sketch 9 → Cut-Revolve 1 (revolve, cut)
    with BuildSketch(Plane(origin=(0, 0, 0), x_dir=(1, 0, 0), z_dir=(0, 1, 0)), mode=Mode.PRIVATE) as cut_revolve_1_sk:
        Polygon((0.55, -22), (0.75, -22), (0.75, -21.65), align=None)
    revolve(cut_revolve_1_sk.sketch.rotate(Axis((0, 0, 22), (0, 0, -1)), 180), axis=Axis((0, 0, 22), (0, 0, -1)), mode=Mode.SUBTRACT)


solid = part.part
